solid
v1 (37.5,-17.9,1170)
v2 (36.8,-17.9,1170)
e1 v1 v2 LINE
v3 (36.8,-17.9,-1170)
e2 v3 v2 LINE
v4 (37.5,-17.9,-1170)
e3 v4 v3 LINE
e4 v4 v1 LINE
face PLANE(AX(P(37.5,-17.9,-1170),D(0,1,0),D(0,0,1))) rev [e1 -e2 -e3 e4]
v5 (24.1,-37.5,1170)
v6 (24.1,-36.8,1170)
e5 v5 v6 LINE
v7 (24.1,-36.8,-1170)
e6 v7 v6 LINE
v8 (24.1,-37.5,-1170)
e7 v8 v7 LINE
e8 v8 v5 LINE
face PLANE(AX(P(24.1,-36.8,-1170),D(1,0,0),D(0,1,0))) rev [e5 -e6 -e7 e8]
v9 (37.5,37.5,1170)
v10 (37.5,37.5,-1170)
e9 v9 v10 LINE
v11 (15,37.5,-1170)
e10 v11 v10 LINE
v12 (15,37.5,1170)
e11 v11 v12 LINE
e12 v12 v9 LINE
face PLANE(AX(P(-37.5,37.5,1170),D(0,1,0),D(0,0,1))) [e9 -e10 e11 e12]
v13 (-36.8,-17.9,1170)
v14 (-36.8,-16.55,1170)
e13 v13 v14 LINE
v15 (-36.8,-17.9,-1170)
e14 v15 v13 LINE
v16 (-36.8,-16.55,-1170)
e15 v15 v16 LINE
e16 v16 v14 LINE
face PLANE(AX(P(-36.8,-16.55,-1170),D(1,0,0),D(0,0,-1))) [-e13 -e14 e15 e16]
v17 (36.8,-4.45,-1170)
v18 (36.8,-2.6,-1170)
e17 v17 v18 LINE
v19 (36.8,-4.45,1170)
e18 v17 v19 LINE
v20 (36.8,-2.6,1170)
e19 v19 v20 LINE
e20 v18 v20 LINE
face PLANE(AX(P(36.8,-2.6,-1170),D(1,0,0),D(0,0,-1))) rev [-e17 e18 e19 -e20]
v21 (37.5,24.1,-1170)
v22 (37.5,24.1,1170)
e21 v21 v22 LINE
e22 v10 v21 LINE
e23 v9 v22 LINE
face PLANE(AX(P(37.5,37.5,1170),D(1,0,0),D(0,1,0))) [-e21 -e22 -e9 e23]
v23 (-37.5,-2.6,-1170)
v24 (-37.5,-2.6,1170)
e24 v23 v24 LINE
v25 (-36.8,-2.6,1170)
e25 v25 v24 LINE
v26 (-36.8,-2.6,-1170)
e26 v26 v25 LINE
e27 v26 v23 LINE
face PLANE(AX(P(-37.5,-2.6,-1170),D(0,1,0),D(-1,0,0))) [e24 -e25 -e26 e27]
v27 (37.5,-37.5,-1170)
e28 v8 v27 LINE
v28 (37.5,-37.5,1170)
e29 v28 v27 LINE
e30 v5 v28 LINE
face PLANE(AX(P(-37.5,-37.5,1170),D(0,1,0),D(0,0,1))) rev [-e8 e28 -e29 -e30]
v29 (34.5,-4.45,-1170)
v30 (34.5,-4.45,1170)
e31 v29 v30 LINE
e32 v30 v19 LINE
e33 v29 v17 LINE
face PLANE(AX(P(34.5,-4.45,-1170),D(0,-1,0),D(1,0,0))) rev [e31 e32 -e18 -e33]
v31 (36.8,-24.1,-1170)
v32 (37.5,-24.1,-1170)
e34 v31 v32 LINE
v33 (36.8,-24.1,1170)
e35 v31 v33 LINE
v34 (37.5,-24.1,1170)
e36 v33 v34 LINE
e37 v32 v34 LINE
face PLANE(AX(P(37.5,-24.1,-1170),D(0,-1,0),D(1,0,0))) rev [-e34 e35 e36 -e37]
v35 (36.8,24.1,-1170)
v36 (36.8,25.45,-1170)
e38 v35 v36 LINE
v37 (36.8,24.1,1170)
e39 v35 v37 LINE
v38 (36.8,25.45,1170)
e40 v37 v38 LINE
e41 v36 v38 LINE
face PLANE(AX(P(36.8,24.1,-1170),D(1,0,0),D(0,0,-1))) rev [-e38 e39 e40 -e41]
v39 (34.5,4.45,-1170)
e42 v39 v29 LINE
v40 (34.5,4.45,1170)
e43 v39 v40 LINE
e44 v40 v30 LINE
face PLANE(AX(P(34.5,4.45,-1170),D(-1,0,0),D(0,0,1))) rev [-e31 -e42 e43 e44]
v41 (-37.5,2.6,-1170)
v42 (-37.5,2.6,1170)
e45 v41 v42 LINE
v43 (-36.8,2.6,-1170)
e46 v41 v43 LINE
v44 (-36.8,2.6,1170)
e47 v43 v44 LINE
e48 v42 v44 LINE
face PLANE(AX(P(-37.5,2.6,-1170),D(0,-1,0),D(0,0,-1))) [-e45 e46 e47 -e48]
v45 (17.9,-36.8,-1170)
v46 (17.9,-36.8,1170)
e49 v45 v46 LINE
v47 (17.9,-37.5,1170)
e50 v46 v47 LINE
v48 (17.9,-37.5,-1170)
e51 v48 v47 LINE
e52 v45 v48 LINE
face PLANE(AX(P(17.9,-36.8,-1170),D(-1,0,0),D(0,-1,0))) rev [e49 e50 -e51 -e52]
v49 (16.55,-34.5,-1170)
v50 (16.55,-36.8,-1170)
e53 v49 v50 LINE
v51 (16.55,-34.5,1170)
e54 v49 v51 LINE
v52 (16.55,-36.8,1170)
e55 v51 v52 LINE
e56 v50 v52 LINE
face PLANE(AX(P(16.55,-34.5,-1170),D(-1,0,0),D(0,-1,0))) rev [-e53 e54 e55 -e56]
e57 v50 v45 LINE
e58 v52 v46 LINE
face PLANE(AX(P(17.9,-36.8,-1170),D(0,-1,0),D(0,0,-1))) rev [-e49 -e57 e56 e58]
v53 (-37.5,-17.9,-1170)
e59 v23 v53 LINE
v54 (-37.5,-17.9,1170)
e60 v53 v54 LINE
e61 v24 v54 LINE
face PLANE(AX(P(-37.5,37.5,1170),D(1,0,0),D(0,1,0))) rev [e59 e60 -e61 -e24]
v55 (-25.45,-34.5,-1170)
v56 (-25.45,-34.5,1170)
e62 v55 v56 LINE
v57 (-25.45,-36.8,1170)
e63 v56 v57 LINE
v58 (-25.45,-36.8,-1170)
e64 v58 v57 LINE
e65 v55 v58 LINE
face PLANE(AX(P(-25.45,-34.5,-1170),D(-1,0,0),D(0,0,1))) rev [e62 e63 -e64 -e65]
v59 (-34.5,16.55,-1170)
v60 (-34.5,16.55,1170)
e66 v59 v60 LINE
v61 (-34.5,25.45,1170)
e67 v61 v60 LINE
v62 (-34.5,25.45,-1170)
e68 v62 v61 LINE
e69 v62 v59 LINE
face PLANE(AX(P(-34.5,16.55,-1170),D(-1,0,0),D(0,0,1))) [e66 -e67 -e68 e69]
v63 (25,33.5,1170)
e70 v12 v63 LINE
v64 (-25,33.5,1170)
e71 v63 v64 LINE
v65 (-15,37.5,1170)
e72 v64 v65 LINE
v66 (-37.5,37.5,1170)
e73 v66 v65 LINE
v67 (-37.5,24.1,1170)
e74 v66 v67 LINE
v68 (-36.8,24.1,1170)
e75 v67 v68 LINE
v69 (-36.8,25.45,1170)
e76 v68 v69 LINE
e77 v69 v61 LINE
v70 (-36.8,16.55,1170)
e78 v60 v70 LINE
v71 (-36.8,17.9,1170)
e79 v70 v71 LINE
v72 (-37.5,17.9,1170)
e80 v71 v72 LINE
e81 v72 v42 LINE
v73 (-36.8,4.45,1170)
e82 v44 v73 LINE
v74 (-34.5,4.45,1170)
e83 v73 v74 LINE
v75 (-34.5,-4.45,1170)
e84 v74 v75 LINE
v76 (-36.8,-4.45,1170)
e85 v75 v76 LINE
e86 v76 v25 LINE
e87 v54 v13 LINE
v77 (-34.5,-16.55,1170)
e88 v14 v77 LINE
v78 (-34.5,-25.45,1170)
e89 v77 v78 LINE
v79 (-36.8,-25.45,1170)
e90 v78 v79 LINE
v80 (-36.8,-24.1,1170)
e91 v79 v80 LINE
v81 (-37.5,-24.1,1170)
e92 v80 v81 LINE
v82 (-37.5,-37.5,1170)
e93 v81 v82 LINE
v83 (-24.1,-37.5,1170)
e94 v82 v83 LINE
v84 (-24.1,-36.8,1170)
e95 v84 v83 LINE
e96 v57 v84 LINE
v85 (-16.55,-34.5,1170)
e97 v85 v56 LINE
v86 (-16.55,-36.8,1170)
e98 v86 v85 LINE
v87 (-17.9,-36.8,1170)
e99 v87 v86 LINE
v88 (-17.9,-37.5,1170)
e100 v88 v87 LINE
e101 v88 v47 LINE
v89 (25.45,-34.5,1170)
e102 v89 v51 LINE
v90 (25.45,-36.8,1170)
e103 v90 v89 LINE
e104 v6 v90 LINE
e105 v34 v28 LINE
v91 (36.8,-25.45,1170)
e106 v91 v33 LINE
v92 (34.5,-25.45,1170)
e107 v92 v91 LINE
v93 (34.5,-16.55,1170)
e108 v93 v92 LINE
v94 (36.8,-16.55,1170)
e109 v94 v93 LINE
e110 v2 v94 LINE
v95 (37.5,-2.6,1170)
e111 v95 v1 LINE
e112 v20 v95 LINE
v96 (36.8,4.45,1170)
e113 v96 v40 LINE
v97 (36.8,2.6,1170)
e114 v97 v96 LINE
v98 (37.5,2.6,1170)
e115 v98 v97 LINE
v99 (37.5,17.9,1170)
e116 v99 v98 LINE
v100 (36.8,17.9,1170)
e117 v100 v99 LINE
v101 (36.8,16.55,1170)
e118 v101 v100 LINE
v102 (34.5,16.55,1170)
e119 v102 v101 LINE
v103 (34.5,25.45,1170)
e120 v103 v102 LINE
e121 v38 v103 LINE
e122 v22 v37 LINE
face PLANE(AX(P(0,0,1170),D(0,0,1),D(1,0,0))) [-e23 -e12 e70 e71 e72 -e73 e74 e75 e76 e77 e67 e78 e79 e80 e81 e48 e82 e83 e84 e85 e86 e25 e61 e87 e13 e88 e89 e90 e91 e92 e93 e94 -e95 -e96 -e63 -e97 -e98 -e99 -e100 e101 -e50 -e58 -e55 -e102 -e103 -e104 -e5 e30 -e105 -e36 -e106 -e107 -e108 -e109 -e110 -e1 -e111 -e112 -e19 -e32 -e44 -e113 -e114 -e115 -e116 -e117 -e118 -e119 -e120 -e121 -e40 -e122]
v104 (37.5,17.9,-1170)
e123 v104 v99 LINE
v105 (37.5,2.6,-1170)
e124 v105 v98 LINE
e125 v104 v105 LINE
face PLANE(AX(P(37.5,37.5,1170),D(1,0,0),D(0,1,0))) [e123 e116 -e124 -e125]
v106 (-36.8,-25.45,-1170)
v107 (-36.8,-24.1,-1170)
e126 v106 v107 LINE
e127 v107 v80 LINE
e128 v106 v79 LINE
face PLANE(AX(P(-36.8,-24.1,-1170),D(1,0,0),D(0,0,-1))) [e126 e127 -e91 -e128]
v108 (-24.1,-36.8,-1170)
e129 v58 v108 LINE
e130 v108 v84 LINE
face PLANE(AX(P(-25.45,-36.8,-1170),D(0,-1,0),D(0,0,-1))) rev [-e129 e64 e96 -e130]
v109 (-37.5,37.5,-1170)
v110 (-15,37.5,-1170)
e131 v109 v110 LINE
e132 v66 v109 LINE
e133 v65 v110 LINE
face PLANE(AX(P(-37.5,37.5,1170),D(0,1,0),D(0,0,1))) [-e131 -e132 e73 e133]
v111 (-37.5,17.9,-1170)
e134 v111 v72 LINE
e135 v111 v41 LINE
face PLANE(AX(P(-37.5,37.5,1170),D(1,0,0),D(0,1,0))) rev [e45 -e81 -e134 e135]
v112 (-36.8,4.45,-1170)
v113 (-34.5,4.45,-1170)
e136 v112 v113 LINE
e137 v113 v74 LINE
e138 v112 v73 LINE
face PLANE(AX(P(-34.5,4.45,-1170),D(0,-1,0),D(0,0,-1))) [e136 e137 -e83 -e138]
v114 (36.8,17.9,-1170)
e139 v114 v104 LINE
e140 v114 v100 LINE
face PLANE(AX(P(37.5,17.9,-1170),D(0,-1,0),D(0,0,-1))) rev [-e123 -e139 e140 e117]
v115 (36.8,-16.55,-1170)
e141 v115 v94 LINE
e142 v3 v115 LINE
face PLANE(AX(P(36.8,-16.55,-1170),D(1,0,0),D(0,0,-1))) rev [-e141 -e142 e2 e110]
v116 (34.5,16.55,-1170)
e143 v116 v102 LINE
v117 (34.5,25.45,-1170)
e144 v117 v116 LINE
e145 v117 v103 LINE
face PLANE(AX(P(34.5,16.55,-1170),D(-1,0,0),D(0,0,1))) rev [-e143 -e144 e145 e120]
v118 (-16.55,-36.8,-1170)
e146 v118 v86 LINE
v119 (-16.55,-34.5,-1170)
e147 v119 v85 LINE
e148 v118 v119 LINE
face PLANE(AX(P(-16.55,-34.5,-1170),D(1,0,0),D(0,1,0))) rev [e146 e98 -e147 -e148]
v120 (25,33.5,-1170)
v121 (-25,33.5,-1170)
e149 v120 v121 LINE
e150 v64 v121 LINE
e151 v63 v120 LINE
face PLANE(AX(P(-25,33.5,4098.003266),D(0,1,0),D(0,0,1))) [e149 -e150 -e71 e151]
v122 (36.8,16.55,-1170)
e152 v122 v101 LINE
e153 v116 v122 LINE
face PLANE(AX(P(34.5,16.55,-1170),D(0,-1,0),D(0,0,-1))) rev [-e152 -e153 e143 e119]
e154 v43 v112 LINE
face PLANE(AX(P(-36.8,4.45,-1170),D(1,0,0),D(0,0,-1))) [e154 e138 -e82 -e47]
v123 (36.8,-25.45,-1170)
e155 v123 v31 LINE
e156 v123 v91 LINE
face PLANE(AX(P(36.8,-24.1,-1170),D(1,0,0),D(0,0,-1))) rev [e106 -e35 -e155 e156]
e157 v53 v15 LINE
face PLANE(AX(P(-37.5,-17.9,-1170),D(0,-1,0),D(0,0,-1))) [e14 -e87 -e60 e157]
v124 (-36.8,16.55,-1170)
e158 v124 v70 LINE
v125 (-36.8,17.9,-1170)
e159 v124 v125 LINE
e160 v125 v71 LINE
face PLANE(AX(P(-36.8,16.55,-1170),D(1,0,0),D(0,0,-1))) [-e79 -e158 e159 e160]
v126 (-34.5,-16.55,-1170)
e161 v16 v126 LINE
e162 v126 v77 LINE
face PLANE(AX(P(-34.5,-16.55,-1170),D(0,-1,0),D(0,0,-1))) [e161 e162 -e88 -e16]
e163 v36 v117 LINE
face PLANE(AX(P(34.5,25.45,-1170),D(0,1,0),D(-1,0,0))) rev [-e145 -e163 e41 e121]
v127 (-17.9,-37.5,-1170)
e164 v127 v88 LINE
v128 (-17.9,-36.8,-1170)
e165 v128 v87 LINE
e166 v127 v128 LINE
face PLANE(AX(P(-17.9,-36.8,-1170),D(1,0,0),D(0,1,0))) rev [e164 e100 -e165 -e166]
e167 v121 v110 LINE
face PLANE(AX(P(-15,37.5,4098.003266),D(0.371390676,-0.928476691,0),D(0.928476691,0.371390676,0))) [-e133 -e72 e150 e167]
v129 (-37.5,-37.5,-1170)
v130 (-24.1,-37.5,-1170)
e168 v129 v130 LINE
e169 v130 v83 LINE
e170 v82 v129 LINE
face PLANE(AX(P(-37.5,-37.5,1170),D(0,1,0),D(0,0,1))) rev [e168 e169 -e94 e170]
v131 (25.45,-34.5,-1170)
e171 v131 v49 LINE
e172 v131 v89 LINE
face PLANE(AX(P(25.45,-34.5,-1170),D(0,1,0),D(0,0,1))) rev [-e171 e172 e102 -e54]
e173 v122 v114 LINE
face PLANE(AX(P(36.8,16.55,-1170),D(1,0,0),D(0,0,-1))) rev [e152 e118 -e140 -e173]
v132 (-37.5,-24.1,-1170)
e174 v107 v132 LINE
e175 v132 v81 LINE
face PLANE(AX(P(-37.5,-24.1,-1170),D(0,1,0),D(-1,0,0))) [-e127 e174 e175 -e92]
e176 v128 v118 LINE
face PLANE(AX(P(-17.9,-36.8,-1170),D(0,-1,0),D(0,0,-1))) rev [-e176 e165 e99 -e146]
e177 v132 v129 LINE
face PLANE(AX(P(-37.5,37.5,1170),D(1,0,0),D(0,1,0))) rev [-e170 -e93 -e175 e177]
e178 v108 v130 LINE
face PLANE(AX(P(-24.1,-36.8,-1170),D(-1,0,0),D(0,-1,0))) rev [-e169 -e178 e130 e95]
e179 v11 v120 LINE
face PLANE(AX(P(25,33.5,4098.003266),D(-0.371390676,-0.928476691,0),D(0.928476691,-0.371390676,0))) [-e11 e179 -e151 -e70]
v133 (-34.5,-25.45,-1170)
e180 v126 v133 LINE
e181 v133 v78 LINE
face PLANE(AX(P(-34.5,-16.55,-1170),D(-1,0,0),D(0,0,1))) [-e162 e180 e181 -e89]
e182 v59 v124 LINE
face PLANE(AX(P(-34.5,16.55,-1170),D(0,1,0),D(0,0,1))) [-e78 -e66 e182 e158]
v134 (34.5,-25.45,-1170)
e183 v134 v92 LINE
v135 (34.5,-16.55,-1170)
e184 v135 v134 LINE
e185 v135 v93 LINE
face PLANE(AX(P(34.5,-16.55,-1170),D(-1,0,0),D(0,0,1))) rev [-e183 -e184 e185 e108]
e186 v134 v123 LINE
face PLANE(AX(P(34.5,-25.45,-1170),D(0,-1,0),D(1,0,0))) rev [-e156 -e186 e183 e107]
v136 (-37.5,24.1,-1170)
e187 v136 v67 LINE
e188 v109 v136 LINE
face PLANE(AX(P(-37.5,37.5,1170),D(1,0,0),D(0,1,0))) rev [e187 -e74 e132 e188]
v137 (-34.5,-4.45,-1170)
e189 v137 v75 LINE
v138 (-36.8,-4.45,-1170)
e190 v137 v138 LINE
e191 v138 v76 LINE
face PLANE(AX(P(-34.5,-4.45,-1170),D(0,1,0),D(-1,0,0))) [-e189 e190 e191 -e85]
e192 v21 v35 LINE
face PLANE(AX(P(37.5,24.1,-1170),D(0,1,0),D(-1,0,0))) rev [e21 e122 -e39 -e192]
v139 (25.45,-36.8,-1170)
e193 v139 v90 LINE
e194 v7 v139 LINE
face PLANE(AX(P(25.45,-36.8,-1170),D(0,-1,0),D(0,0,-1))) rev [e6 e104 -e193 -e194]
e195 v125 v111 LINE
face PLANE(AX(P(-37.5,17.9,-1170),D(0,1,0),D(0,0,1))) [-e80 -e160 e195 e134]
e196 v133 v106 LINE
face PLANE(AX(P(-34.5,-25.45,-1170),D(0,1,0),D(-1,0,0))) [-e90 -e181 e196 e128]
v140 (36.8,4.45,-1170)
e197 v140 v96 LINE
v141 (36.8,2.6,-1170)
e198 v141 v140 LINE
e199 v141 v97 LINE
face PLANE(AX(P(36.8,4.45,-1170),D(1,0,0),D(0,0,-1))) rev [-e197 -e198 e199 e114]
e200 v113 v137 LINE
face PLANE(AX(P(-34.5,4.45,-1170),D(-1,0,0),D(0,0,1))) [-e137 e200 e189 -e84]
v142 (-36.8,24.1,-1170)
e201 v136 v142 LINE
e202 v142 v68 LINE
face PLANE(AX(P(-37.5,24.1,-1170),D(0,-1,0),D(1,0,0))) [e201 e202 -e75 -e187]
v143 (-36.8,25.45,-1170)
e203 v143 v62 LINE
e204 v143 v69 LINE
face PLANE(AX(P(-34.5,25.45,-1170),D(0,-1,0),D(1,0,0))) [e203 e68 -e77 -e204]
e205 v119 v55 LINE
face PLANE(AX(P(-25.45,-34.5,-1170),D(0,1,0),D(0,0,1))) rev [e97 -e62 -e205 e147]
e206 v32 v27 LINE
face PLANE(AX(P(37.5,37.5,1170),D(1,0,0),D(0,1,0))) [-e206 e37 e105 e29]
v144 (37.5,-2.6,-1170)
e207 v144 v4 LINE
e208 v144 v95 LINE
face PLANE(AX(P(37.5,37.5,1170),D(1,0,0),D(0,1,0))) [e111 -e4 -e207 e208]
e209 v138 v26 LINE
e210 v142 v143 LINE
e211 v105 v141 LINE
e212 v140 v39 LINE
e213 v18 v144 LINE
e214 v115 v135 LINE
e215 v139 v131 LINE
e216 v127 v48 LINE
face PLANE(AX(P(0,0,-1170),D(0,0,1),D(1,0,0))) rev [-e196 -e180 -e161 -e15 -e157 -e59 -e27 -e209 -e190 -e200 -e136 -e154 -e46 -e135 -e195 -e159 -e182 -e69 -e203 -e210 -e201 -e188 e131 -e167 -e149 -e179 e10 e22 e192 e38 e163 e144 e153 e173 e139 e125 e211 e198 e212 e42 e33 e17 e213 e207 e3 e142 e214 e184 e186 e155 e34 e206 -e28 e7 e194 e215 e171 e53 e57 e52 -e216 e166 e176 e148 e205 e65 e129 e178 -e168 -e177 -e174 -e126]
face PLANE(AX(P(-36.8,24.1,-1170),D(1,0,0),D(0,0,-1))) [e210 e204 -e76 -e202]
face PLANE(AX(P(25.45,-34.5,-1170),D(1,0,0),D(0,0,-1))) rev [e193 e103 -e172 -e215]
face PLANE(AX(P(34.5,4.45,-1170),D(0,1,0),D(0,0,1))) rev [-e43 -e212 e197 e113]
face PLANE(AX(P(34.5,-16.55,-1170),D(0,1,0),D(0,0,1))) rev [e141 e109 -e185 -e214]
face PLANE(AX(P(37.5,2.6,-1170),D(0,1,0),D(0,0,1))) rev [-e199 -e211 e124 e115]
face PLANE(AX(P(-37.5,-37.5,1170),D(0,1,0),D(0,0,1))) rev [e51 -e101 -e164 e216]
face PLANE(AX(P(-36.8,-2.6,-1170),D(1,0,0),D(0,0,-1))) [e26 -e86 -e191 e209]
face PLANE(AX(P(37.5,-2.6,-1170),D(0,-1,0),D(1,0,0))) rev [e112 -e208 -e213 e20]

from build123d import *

# Parameters (mm, degrees)
SKETCH_1_W               = 75
SKETCH_1_H               = 75
EXTRUDE_1_DEPTH          = 1170
CUT_EXTRUDE_1_DEPTH      = 1170
CUT_EXTRUDE_2_DEPTH      = 2340
CUT_EXTRUDE_3_DEPTH      = 2341.600884388
CUT_EXTRUDE_3_DEPTH_BACK = 2341.600884388


with BuildPart() as part:
    # 草图1 → 凸台-拉伸1 (new, symmetric)
    with BuildSketch(Plane.XY):
        Rectangle(SKETCH_1_W, SKETCH_1_H)
    extrude(amount=EXTRUDE_1_DEPTH, both=True)

    # 草图2 → 切除-拉伸1 (cut, symmetric)
    with BuildSketch(Plane.XY):
        Polygon((-17.9, -36.8), (-16.55, -36.8), (-16.55, -34.5), (-25.45, -34.5), (-25.45, -36.8), (-24.1, -36.8), (-24.1, -37.5), (-17.9, -37.5), align=None)
        Polygon((16.55, -34.5), (16.55, -36.8), (17.9, -36.8), (17.9, -37.5), (24.1, -37.5), (24.1, -36.8), (25.45, -36.8), (25.45, -34.5), align=None)
    extrude(amount=CUT_EXTRUDE_1_DEPTH, both=True, mode=Mode.SUBTRACT)

    # 草图3 → 切除-拉伸2 (cut)
    with BuildSketch(Plane.XY.offset(1170)):
        Polygon((37.5, 2.6), (36.8, 2.6), (36.8, 4.45), (34.5, 4.45), (34.5, -4.45), (36.8, -4.45), (36.8, -2.6), (37.5, -2.6), align=None)
        Polygon((37.5, -17.9), (36.8, -17.9), (36.8, -16.55), (34.5, -16.55), (34.5, -25.45), (36.8, -25.45), (36.8, -24.1), (37.5, -24.1), align=None)
        Polygon((36.8, 24.1), (36.8, 25.45), (34.5, 25.45), (34.5, 16.55), (36.8, 16.55), (36.8, 17.9), (37.5, 17.9), (37.5, 24.1), align=None)
    cut_extrude_2 = extrude(amount=-CUT_EXTRUDE_2_DEPTH, mode=Mode.SUBTRACT)

    # 镜向1: 切除-拉伸2 across plane
    add(cut_extrude_2.mirror(Plane(origin=(0, 0, 0), x_dir=(0, 0, 1), z_dir=(1, 0, 0))), mode=Mode.SUBTRACT)

    # 草图4 → 切除-拉伸3 (cut, two sides: drawn at the far end of the back side and taken through both)
    with BuildSketch(Plane.XY.offset(1170).offset(-CUT_EXTRUDE_3_DEPTH_BACK)):
        Polygon((164.287302387, 109.214920955), (-15, 37.5), (-25, 33.5), (25, 33.5), (15, 37.5), (-164.287302387, 109.214920955), (-164.287302387, -276.981747517), (164.287302387, -276.981747517), align=None)
    extrude(amount=CUT_EXTRUDE_3_DEPTH + CUT_EXTRUDE_3_DEPTH_BACK, mode=Mode.SUBTRACT)


solid = part.part
